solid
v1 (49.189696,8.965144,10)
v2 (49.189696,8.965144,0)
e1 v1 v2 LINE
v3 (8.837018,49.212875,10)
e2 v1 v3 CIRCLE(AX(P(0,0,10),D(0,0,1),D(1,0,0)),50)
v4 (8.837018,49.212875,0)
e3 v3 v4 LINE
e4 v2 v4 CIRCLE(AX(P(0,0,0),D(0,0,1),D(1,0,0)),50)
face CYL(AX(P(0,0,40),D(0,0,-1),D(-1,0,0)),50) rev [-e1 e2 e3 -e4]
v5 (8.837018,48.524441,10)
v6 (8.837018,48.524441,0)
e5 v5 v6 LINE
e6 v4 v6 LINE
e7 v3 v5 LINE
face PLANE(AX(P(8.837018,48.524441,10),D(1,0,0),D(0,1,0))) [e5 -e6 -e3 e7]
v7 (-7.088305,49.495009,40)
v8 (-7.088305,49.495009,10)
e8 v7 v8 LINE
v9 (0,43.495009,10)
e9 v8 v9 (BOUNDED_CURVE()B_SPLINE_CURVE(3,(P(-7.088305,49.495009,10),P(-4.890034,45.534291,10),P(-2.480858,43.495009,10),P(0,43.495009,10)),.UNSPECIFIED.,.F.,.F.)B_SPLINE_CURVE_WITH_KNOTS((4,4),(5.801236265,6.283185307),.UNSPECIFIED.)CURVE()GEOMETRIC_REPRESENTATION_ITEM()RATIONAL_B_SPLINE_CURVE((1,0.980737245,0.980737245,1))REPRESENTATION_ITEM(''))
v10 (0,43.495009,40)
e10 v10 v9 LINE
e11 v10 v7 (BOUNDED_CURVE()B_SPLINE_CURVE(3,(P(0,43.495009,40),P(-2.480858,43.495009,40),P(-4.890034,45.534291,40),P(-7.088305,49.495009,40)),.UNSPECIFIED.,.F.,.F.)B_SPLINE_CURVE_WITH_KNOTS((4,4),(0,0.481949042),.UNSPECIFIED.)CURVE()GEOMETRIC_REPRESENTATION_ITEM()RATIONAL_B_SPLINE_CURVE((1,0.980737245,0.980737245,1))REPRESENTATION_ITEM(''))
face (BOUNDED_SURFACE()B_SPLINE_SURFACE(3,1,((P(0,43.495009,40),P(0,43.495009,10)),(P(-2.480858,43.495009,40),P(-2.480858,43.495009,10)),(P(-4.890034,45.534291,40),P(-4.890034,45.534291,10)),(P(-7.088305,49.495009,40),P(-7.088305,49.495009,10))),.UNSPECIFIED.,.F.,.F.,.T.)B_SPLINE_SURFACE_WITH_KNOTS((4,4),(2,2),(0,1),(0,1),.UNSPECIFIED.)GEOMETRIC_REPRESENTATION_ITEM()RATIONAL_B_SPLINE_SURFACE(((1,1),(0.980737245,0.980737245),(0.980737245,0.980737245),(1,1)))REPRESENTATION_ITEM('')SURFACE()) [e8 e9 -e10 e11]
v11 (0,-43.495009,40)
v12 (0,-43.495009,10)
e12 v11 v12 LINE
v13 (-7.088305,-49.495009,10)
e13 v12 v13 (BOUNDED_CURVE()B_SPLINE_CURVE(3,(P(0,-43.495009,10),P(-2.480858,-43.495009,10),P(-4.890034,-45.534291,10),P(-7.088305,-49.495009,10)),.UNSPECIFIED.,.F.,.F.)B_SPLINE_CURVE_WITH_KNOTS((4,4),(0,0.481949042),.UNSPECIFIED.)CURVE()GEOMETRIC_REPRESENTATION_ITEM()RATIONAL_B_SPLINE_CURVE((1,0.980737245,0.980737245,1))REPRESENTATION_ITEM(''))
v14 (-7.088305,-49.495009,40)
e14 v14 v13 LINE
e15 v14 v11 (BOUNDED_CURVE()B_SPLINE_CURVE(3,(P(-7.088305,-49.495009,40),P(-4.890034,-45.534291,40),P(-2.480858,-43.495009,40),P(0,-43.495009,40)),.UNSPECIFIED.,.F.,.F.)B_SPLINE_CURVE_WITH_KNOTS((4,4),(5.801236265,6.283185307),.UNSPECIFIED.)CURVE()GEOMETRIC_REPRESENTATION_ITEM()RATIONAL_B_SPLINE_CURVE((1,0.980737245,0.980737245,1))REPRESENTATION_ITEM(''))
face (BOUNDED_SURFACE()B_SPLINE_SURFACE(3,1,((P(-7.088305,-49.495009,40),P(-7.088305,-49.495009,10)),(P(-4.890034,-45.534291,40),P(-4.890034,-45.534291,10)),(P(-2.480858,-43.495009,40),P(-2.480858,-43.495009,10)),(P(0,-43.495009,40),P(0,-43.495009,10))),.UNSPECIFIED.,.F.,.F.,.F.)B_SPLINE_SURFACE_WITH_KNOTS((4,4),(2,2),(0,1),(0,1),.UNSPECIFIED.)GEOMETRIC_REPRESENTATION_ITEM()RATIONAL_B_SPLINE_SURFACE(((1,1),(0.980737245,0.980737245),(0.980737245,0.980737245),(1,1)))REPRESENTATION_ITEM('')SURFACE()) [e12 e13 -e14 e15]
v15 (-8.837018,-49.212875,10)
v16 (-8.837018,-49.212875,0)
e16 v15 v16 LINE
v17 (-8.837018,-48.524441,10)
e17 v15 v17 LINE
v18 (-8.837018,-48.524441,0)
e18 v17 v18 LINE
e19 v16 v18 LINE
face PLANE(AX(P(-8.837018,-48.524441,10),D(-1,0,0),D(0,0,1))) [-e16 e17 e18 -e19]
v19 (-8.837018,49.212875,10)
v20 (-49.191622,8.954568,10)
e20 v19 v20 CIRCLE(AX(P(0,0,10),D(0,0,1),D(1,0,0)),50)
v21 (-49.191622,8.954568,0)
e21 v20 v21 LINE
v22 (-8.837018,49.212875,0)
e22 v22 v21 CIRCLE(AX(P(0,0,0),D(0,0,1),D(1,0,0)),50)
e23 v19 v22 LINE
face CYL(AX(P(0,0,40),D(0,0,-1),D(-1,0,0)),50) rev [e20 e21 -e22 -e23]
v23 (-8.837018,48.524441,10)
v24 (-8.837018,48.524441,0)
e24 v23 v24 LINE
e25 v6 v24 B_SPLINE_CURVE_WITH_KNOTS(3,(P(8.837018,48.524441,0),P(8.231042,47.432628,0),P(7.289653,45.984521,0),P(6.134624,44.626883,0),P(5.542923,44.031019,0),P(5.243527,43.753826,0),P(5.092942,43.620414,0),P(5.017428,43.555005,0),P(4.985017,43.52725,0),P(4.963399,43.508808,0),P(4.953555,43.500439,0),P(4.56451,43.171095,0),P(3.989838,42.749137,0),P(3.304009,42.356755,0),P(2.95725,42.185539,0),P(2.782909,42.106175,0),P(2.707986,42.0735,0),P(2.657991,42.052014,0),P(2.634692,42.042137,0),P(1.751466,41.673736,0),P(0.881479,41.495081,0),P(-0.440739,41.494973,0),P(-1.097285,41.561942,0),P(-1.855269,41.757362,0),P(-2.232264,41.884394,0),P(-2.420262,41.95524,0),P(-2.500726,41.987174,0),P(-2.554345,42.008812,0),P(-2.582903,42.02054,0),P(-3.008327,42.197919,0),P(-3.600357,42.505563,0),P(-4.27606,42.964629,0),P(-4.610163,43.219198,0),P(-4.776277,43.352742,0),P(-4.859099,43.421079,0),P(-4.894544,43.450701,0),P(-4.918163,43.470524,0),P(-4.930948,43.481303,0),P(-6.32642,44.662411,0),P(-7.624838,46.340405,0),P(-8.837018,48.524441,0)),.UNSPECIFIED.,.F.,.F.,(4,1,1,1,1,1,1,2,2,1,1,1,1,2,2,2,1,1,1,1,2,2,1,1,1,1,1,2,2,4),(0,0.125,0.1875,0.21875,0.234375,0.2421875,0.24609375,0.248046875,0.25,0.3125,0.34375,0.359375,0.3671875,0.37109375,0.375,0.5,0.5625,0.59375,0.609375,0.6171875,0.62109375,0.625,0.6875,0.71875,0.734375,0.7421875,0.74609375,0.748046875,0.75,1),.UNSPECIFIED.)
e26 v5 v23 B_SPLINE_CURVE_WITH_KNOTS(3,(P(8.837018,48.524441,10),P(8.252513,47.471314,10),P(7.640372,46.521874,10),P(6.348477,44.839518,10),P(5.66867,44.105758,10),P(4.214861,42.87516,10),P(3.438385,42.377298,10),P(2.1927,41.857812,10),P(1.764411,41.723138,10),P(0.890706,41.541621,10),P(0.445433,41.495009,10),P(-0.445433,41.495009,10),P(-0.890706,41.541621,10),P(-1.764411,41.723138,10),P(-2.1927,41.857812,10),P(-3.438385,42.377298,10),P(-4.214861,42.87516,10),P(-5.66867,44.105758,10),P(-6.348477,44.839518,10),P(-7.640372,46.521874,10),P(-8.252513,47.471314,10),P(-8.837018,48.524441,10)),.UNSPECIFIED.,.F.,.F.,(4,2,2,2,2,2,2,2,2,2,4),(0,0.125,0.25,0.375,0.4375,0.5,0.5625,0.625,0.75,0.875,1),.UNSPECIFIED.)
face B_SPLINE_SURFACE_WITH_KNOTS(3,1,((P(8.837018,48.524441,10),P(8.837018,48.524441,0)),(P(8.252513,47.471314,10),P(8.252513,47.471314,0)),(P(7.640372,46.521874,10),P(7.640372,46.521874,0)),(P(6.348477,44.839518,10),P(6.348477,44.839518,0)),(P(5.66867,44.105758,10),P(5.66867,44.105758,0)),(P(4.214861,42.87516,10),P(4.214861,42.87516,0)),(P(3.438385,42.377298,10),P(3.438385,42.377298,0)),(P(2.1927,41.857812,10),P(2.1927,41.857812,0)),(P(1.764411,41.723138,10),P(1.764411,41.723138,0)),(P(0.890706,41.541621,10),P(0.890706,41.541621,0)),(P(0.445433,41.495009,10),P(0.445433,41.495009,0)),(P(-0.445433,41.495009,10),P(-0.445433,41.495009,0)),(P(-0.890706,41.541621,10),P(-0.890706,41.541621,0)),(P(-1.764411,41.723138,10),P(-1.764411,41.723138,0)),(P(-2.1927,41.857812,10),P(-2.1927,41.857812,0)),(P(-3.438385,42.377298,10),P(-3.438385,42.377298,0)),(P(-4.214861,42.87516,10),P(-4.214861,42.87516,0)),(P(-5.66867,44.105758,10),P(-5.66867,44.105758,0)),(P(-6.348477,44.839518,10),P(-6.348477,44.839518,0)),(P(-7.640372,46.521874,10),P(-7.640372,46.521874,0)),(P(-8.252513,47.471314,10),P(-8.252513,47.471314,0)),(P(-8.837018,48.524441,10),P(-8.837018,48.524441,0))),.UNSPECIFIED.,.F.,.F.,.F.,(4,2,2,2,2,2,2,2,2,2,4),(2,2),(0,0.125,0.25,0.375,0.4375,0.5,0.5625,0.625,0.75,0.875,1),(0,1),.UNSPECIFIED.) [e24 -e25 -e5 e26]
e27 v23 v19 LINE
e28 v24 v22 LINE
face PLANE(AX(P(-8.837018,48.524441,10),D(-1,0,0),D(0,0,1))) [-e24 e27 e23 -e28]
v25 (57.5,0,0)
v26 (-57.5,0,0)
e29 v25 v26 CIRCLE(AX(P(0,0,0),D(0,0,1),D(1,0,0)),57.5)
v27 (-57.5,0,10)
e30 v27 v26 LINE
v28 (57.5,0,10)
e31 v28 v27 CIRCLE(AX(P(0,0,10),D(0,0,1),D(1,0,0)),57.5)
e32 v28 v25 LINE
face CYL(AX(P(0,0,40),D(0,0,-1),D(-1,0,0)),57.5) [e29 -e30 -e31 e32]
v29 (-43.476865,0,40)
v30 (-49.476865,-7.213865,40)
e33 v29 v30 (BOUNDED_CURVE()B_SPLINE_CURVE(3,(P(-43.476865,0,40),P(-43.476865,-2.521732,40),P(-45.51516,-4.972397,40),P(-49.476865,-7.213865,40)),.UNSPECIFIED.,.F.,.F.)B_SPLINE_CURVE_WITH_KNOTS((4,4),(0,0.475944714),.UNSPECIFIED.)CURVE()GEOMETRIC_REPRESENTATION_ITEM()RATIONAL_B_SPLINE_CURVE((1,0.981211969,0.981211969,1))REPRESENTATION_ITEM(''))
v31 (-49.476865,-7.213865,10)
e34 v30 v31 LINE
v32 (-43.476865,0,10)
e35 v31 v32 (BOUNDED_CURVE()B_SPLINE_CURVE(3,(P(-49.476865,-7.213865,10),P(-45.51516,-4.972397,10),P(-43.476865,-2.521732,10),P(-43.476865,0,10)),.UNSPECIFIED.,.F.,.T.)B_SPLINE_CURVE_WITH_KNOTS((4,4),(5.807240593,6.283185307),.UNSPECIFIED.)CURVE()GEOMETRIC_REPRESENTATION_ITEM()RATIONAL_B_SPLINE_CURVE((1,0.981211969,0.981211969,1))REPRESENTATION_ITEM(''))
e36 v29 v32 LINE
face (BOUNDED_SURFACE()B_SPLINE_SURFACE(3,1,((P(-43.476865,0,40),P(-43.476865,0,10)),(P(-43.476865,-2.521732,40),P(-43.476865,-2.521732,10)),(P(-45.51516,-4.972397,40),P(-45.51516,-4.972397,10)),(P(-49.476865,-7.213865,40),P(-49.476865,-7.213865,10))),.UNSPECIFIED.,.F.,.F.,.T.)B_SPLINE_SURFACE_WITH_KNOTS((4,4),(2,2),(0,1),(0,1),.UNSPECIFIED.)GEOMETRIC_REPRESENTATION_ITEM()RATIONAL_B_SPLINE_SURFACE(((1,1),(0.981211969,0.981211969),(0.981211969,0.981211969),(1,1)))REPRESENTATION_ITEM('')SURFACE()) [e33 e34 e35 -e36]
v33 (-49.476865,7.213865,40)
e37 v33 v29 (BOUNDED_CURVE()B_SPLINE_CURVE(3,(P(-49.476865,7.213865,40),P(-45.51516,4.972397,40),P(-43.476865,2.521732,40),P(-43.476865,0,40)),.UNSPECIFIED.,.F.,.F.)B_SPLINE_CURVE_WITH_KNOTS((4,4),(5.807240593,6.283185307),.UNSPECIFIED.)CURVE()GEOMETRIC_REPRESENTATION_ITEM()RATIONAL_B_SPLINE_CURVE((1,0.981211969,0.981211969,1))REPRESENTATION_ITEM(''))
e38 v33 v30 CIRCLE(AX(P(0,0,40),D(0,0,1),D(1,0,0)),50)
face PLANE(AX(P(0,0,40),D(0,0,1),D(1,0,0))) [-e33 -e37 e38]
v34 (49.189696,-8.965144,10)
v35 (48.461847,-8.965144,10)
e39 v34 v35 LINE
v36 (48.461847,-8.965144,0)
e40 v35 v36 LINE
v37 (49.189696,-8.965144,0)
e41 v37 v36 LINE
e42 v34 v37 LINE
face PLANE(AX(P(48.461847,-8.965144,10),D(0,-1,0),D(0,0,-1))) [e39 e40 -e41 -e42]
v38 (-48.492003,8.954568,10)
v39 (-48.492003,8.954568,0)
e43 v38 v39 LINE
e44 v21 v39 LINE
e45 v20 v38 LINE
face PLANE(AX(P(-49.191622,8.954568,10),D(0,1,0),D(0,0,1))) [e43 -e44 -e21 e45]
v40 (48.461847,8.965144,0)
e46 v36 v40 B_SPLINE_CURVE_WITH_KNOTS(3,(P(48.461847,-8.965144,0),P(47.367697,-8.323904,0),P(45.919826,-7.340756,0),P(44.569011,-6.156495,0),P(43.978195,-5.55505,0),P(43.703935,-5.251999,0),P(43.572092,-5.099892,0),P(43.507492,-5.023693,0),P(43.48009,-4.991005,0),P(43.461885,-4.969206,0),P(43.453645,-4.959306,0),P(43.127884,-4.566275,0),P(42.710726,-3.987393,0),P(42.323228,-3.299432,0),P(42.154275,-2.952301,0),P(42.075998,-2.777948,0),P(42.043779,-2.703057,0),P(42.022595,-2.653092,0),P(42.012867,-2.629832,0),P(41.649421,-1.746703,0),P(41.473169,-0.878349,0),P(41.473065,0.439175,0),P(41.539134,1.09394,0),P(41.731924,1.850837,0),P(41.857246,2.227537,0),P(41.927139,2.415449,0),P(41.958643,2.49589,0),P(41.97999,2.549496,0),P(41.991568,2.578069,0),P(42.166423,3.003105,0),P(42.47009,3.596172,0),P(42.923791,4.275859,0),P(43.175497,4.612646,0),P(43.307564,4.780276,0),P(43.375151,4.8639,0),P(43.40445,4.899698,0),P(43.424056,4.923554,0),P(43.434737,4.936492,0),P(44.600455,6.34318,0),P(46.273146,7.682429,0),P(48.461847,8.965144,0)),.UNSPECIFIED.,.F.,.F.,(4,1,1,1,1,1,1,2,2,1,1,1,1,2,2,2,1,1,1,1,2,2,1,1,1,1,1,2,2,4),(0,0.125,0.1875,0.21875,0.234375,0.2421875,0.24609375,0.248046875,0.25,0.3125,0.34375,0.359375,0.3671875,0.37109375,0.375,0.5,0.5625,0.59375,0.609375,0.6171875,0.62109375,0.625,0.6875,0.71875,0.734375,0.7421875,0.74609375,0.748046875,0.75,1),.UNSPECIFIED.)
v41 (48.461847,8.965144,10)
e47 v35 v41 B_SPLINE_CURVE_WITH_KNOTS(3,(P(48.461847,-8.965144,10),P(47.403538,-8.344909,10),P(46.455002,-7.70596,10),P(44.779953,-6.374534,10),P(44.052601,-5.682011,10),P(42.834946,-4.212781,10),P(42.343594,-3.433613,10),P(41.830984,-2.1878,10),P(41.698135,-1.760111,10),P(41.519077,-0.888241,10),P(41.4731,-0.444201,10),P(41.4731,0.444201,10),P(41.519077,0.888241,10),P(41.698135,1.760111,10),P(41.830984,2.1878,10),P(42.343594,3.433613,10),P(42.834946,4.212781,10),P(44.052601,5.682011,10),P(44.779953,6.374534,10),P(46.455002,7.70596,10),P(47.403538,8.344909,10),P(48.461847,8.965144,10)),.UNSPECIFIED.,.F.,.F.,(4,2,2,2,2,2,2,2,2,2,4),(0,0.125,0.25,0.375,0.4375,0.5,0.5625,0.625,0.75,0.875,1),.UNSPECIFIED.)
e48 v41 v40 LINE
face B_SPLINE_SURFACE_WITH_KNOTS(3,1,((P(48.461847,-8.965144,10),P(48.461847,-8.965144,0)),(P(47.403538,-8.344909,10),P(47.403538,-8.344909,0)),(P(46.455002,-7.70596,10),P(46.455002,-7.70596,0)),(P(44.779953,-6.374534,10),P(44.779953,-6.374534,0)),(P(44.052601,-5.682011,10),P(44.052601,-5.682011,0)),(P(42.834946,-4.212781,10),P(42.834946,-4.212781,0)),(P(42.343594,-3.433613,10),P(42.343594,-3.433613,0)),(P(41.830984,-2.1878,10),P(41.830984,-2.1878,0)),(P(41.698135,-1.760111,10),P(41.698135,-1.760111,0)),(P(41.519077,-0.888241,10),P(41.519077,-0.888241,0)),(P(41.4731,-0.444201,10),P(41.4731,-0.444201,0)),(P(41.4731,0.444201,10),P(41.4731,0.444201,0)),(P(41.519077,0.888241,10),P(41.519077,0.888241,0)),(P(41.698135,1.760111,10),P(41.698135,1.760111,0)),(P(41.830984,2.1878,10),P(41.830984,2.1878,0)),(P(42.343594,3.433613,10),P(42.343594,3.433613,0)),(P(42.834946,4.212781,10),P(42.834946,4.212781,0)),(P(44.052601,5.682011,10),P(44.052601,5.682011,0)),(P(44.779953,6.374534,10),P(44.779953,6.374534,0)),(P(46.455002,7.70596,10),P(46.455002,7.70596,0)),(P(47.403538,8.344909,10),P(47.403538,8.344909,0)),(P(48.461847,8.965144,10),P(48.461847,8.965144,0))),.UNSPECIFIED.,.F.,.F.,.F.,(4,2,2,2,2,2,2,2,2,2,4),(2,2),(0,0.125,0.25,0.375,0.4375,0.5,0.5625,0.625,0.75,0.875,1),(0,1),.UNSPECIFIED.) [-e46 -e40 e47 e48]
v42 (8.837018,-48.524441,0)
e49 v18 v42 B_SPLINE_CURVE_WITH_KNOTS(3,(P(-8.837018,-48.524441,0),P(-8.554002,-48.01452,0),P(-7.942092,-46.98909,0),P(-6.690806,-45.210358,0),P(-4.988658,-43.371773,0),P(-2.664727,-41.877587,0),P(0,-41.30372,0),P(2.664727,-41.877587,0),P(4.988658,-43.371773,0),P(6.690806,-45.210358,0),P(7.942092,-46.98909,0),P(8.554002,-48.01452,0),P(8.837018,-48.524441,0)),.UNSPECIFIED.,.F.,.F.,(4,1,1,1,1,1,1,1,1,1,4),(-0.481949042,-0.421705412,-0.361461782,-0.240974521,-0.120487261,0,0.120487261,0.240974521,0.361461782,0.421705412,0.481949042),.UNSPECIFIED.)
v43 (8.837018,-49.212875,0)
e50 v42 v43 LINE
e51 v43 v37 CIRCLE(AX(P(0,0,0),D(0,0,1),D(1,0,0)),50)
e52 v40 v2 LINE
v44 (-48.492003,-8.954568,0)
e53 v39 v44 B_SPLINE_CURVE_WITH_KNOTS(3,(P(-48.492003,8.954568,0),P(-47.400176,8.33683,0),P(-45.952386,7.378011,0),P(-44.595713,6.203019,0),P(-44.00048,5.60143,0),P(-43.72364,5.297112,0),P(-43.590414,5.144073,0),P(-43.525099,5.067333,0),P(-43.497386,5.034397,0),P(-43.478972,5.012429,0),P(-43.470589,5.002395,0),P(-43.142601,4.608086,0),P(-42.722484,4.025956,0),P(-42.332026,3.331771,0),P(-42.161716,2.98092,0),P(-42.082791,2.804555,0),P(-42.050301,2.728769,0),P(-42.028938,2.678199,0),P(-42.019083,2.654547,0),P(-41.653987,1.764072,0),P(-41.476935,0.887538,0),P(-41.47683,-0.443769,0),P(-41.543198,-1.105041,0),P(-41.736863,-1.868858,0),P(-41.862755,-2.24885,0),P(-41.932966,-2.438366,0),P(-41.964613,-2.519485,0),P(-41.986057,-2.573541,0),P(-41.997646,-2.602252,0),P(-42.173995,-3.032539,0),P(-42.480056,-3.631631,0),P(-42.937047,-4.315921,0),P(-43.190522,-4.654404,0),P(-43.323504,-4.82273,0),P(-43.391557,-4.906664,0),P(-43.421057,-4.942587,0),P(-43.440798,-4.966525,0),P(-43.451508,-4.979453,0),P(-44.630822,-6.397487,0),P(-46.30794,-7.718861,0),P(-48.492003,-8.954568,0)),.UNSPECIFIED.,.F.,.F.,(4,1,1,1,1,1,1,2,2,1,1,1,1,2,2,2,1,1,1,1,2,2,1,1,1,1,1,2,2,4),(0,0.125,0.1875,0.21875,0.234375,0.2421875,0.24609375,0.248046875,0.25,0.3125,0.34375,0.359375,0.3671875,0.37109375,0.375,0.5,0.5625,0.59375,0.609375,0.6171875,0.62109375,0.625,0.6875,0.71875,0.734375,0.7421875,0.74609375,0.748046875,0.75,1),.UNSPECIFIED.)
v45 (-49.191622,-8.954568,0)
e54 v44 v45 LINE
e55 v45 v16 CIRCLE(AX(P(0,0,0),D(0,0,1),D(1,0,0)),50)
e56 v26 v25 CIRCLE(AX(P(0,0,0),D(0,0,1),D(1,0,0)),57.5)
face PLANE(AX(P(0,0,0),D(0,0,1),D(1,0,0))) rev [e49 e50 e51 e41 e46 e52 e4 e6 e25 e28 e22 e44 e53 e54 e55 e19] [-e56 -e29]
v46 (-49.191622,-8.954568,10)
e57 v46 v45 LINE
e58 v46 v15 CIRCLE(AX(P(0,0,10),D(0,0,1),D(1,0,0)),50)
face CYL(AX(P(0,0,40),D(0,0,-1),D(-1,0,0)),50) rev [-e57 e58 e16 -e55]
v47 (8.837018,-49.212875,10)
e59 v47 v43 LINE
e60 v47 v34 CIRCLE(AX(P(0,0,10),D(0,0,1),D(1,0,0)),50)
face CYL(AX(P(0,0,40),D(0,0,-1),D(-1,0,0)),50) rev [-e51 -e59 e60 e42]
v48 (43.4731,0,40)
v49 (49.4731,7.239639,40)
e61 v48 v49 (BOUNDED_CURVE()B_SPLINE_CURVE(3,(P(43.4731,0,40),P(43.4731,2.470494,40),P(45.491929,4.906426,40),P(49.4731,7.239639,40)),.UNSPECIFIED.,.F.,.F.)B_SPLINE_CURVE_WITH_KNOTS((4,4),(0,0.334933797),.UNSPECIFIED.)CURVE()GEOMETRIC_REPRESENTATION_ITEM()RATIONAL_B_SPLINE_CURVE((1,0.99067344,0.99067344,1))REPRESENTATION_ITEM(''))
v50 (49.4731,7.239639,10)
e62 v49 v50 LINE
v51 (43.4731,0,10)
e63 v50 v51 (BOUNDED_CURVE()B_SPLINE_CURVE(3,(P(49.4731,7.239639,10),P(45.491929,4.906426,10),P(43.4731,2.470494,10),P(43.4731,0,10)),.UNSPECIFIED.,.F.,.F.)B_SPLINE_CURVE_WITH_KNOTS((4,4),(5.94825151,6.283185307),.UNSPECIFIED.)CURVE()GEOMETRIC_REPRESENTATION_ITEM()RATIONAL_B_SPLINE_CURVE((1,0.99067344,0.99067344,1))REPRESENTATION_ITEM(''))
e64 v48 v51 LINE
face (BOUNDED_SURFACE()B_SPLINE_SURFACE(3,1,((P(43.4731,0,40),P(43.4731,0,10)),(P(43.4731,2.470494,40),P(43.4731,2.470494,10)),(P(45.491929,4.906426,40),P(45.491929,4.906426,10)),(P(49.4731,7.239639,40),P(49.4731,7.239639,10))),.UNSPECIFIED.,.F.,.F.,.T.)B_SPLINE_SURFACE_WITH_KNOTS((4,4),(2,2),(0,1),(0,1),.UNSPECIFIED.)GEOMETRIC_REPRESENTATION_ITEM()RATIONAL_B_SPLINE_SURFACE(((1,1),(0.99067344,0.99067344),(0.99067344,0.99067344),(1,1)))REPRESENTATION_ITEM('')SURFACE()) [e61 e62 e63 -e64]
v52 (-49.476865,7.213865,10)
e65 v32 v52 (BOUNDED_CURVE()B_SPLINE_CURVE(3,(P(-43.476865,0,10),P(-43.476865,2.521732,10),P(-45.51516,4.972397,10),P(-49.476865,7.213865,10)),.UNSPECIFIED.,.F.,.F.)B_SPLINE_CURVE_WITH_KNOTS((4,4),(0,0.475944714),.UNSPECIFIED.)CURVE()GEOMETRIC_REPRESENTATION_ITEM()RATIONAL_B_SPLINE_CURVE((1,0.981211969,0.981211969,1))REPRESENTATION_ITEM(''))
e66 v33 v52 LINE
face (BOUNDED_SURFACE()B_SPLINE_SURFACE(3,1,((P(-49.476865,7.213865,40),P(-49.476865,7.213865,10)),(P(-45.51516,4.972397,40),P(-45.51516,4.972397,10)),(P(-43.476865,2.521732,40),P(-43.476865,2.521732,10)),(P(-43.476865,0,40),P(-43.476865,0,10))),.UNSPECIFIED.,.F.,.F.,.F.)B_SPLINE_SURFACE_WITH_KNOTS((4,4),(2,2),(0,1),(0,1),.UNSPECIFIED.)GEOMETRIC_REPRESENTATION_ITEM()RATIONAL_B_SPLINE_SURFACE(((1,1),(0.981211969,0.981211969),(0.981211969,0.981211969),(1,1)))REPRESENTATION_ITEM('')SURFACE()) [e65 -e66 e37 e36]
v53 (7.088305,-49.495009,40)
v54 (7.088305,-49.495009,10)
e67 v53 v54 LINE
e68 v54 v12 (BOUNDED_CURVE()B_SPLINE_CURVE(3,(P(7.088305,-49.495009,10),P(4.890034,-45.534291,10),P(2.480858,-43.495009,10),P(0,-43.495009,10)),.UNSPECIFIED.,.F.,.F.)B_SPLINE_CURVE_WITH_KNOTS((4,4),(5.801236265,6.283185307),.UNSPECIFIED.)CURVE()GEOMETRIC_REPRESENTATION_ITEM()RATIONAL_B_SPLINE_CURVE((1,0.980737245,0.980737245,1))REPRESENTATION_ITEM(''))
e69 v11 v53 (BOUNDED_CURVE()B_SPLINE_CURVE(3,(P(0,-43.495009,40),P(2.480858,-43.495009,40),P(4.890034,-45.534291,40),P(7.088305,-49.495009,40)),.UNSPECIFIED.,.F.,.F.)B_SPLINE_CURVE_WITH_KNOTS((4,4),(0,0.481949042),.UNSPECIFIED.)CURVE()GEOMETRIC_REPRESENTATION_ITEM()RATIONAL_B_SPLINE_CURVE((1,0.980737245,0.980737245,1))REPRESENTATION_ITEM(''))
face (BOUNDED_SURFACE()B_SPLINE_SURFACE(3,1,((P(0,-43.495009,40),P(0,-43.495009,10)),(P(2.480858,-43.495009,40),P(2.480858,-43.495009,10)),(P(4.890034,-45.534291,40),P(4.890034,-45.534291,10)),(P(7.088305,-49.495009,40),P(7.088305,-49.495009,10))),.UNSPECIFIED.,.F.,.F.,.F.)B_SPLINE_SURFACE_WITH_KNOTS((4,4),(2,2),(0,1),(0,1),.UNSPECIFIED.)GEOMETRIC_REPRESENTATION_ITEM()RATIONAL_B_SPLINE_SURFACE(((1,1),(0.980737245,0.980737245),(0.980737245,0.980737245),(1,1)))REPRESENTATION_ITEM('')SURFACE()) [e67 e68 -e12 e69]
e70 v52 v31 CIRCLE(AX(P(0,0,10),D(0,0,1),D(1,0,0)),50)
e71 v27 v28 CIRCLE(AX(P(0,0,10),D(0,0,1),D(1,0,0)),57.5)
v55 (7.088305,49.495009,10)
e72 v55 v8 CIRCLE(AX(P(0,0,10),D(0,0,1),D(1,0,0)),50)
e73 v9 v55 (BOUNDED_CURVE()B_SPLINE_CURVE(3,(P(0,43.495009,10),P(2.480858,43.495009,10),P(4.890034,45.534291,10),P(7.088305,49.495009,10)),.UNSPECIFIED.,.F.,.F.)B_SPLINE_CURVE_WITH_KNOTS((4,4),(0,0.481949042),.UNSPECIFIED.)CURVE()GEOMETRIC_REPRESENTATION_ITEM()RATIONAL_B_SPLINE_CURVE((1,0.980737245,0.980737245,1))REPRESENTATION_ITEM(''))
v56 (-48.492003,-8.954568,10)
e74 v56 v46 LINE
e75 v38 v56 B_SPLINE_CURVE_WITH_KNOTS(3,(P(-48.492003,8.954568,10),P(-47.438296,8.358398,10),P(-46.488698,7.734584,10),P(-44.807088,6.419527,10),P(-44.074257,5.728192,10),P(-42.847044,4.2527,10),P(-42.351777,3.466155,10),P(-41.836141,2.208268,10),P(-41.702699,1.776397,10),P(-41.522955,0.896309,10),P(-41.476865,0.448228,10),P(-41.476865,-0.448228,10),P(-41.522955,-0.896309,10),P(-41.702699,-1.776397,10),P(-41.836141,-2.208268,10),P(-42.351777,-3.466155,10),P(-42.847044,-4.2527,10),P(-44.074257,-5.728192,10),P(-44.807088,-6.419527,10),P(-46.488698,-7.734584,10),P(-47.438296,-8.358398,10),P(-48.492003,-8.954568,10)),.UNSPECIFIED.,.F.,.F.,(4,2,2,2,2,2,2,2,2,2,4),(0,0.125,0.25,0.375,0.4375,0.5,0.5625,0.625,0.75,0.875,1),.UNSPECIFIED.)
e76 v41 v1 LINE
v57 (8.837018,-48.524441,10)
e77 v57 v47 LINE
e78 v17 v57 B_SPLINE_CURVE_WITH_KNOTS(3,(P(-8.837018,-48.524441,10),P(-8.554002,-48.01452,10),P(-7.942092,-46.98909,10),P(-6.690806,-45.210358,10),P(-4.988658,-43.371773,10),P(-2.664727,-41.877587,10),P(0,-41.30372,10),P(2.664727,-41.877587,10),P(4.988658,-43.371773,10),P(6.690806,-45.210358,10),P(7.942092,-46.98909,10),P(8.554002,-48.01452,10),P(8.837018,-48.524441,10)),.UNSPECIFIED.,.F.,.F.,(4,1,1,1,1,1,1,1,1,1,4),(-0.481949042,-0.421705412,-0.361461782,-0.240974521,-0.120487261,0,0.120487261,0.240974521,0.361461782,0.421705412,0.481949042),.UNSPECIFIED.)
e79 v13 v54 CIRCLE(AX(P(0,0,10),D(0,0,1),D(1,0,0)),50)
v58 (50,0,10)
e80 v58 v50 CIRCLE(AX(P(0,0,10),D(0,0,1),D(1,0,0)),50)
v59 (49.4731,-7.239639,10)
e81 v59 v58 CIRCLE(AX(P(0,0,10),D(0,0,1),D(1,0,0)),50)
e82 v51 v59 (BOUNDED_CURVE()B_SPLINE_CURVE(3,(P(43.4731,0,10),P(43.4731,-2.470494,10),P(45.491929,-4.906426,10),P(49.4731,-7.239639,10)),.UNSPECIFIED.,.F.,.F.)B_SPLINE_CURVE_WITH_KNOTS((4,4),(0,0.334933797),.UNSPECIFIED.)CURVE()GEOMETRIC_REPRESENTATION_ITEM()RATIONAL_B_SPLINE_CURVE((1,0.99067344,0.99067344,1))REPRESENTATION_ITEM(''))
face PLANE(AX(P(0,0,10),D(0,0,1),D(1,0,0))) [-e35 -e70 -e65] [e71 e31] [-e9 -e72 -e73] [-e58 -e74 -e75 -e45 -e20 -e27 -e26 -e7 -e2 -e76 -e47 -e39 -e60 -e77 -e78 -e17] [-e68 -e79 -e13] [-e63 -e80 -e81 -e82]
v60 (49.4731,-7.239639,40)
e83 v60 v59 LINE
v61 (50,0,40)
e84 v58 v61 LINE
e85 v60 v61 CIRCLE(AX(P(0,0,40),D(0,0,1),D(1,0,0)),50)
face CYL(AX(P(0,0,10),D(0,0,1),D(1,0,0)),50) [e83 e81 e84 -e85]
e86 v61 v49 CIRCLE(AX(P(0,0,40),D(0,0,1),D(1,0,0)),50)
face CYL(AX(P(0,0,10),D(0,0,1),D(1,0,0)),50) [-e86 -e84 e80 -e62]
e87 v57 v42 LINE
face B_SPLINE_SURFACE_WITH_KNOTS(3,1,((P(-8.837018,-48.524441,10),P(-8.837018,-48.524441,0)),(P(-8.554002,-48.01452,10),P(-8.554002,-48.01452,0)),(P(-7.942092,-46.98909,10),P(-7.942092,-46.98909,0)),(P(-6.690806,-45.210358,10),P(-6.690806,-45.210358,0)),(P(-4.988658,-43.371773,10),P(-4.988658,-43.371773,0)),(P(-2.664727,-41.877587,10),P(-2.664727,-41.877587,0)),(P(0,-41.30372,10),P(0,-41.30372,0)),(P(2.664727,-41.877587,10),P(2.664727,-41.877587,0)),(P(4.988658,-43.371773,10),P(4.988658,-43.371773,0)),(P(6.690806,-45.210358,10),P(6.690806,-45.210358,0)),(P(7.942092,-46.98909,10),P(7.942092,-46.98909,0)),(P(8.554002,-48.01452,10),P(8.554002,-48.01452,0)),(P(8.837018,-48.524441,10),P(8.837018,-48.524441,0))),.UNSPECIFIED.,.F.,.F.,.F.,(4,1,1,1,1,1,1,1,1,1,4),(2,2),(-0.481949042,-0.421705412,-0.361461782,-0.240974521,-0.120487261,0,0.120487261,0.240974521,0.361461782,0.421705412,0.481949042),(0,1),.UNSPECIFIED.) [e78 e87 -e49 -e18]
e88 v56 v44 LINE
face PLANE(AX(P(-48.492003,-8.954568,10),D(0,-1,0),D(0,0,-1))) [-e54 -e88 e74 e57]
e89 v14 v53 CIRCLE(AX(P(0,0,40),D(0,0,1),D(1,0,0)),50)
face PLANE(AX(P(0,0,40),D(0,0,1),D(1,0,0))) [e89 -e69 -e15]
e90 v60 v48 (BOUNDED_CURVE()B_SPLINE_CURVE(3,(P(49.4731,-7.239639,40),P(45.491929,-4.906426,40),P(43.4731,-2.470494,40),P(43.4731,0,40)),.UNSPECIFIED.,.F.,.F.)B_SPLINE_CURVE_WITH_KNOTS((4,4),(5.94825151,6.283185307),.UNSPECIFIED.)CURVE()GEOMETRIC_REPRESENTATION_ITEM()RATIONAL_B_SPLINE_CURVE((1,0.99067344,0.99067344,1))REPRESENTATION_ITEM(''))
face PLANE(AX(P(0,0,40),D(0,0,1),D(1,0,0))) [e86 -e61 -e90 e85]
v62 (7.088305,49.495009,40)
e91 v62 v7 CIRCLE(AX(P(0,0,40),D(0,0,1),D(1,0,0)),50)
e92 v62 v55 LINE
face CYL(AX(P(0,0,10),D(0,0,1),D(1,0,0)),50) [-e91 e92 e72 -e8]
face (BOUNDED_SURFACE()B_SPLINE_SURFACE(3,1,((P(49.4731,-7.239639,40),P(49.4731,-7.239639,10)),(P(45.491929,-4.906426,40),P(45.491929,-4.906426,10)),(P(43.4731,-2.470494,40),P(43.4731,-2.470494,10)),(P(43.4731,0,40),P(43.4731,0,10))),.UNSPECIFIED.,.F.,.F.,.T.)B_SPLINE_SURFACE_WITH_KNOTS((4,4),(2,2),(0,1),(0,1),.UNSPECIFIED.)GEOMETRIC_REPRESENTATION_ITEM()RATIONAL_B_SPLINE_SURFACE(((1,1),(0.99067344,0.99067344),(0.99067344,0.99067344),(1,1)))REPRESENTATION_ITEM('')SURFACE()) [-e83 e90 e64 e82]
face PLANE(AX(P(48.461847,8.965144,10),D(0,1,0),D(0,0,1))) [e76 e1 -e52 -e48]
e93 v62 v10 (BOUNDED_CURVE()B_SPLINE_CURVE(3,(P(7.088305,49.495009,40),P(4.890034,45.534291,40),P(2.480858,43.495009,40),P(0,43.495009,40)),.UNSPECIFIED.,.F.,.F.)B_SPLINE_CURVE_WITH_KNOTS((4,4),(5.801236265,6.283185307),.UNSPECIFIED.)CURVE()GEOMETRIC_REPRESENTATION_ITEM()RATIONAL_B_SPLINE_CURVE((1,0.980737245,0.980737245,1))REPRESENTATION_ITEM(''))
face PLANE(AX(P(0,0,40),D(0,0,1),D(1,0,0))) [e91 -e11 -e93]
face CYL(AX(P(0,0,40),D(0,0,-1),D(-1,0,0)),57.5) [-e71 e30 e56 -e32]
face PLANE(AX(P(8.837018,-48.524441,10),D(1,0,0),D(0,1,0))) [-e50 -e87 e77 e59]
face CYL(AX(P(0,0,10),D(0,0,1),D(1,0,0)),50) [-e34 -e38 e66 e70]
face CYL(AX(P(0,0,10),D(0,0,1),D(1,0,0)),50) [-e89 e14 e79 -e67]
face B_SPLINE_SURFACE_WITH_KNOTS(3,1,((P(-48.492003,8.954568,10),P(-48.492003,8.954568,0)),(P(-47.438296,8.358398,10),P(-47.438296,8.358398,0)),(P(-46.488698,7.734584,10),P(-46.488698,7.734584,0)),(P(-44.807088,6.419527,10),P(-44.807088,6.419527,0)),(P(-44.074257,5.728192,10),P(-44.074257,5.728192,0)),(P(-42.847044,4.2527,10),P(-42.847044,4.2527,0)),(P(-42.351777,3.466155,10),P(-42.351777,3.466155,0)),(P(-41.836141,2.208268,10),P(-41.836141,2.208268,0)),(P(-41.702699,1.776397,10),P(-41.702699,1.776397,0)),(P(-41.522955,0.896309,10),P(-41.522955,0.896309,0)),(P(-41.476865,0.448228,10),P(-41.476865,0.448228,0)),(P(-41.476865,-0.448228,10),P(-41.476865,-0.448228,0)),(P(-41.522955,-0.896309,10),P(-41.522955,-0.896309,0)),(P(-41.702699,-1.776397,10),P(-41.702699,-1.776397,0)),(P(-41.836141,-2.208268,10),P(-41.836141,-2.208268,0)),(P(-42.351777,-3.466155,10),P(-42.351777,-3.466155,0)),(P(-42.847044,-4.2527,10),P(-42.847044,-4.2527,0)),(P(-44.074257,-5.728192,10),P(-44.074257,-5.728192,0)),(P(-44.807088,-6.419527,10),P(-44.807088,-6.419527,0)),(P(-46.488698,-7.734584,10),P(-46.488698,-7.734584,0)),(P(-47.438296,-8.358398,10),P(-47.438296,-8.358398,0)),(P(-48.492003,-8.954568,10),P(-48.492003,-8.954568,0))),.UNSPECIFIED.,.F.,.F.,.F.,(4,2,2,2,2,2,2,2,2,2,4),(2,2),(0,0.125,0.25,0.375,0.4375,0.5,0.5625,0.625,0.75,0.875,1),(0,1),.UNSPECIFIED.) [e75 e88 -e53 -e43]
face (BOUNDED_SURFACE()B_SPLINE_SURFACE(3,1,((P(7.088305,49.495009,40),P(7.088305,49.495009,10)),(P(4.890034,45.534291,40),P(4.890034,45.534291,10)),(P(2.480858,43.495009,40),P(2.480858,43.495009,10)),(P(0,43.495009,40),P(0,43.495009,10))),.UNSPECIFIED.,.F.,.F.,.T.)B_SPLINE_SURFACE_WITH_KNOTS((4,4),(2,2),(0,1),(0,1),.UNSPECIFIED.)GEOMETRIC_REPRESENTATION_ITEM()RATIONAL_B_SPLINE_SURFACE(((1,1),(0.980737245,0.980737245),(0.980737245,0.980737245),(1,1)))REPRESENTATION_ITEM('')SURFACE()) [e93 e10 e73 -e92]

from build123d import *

# Parameters (mm, degrees)
SKETCH_1_R          = 57.5
EXTRUDE_1_DEPTH     = 40
CUT_EXTRUDE_START   = -30
SKETCH_2_R          = 60
SKETCH_2_R_2        = 50
CUT_EXTRUDE_3_DEPTH = 30
EXTRUDE_3_DEPTH     = 10
EXTRUDE_4_DEPTH     = 10
EXTRUDE_5_DEPTH     = 10
EXTRUDE_6_DEPTH     = 10


with BuildPart() as part:
    # 草图1 → 拉伸1 (new body)
    with BuildSketch(Plane.XY):
        Circle(SKETCH_1_R)
        with BuildLine():
            ThreePointArc((-7.088304974, 49.495009169), (-35.310457237, 35.400163978), (-49.476864779, 7.213865238))
            add(Edge.make_bspline(
                [(-49.476864779, -7.213865238), (-36.726647454, 0), (-49.476864779, 7.213865238)],
                knots=[5.807240593, 5.807240593, 5.807240593, 6.759130021, 6.759130021, 6.759130021], degree=2, weights=[1, 0.888860271, 1]))
            ThreePointArc((-49.476864779, -7.213865238), (-35.310457237, -35.400163978), (-7.088304974, -49.495009169))
            add(Edge.make_bspline(
                [(7.088304974, -49.495009169), (0, -36.723712512), (-7.088304974, -49.495009169)],
                knots=[5.801236265, 5.801236265, 5.801236265, 6.76513435, 6.76513435, 6.76513435], degree=2, weights=[1, 0.886093211, 1]))
            ThreePointArc((7.088304974, -49.495009169), (35.301235246, -35.409360205), (49.473100028, -7.239639051))
            add(Edge.make_bspline(
                [(49.473100028, 7.239639051), (37.120075632, 0), (49.473100028, -7.239639051)],
                knots=[2.806658856, 2.806658856, 2.806658856, 3.476526451, 3.476526451, 3.476526451], degree=2, weights=[1, 0.944432073, 1]))
            ThreePointArc((49.473100028, 7.239639051), (35.301235246, 35.409360205), (7.088304974, 49.495009169))
            add(Edge.make_bspline(
                [(-7.088304974, 49.495009169), (0, 36.723712512), (7.088304974, 49.495009169)],
                knots=[2.659643611, 2.659643611, 2.659643611, 3.623541696, 3.623541696, 3.623541696], degree=2, weights=[1, 0.886093211, 1]))
        make_face(mode=Mode.SUBTRACT)
    extrude(amount=EXTRUDE_1_DEPTH)

    # 草图2 → 拉伸3 (cut)
    with BuildSketch(Plane.XY.offset(40).offset(CUT_EXTRUDE_START)):
        Circle(SKETCH_2_R)
        Circle(SKETCH_2_R_2, mode=Mode.SUBTRACT)
    extrude(amount=CUT_EXTRUDE_3_DEPTH, mode=Mode.SUBTRACT)

    # 草图5 → 凸台-拉伸3 (add)
    with BuildSketch(Plane(origin=(0, 0, 0), x_dir=(-1, 0, 0), z_dir=(0, 0, -1))):
        with BuildLine():
            Line((49.191622289, 8.954568475), (48.492003246, 8.954568475))
            add(Edge.make_bspline(
                [(48.492003246, 8.954568475), (47.438295788, 8.358397963), (46.488698256, 7.73458393), (44.807087954, 6.419527471), (44.074256872, 5.72819176), (42.847043729, 4.252700055), (42.351776591, 3.466154718), (41.836140902, 2.208267679), (41.702698746, 1.776396531), (41.522955051, 0.896309015), (41.476864779, 0.448228181), (41.476864779, -0.448228181), (41.522955051, -0.896309015), (41.702698746, -1.776396531), (41.836140902, -2.208267679), (42.351776591, -3.466154718), (42.847043729, -4.252700055), (44.074256872, -5.72819176), (44.807087954, -6.419527471), (46.488698256, -7.73458393), (47.438295788, -8.358397963), (48.492003246, -8.954568475)],
                knots=[0, 0, 0, 0, 0.125, 0.125, 0.25, 0.25, 0.375, 0.375, 0.4375, 0.4375, 0.5, 0.5, 0.5625, 0.5625, 0.625, 0.625, 0.75, 0.75, 0.875, 0.875, 1, 1, 1, 1], degree=3))
            Line((48.492003246, -8.954568475), (49.191622289, -8.954568475))
            ThreePointArc((49.191622289, -8.954568475), (49.341920281, -8.085474816), (49.476864779, -7.213865238))
            add(Edge.make_bspline(
                [(49.476864779, 7.213865238), (36.726647454, 0), (49.476864779, -7.213865238)],
                knots=[5.807240593, 5.807240593, 5.807240593, 6.759130021, 6.759130021, 6.759130021], degree=2, weights=[1, 0.888860271, 1]))
            ThreePointArc((49.476864779, 7.213865238), (49.341920281, 8.085474816), (49.191622289, 8.954568475))
        make_face()
    extrude(amount=-EXTRUDE_3_DEPTH)

    # 草图7 → 凸台-拉伸4 (add)
    with BuildSketch(Plane(origin=(0, 0, 0), x_dir=(-1, 0, 0), z_dir=(0, 0, -1))):
        with BuildLine():
            Line((-8.837018132, -48.524441143), (-8.837018132, -49.212875455))
            ThreePointArc((-8.837018132, -49.212875455), (-7.963911028, -49.361686774), (-7.088304974, -49.495009169))
            add(Edge.make_bspline(
                [(7.088304974, -49.495009169), (0, -36.723712512), (-7.088304974, -49.495009169)],
                knots=[5.801236265, 5.801236265, 5.801236265, 6.76513435, 6.76513435, 6.76513435], degree=2, weights=[1, 0.886093211, 1]))
            ThreePointArc((7.088304974, -49.495009169), (7.963911028, -49.361686774), (8.837018132, -49.212875455))
            Line((8.837018132, -49.212875455), (8.837018132, -48.524441143))
            add(Edge.make_bspline(
                [(8.837018132, -48.524441143), (8.554002496, -48.014519989), (7.94209171, -46.989090119), (6.690805785, -45.210357531), (4.988657794, -43.371772875), (2.66472736, -41.877587359), (0, -41.303720073), (-2.66472736, -41.877587359), (-4.988657794, -43.371772875), (-6.690805785, -45.210357531), (-7.94209171, -46.989090119), (-8.554002496, -48.014519989), (-8.837018132, -48.524441143)],
                knots=[-0.481949042, -0.481949042, -0.481949042, -0.481949042, -0.421705412, -0.361461782, -0.240974521, -0.120487261, 0, 0.120487261, 0.240974521, 0.361461782, 0.421705412, 0.481949042, 0.481949042, 0.481949042, 0.481949042], degree=3))
        make_face()
    extrude(amount=-EXTRUDE_4_DEPTH)

    # 草图8 → 凸台-拉伸5 (add)
    with BuildSketch(Plane(origin=(0, 0, 0), x_dir=(-1, 0, 0), z_dir=(0, 0, -1))):
        with BuildLine():
            Line((-48.461847021, 8.965144008), (-49.189696003, 8.965144008))
            ThreePointArc((-49.189696003, 8.965144008), (-49.33894174, 8.103630542), (-49.473100028, 7.239639051))
            add(Edge.make_bspline(
                [(-49.473100028, -7.239639051), (-37.120075632, 0), (-49.473100028, 7.239639051)],
                knots=[2.806658856, 2.806658856, 2.806658856, 3.476526451, 3.476526451, 3.476526451], degree=2, weights=[1, 0.944432073, 1]))
            ThreePointArc((-49.473100028, -7.239639051), (-49.33894174, -8.103630542), (-49.189696003, -8.965144008))
            Line((-49.189696003, -8.965144008), (-48.461847021, -8.965144008))
            add(Edge.make_bspline(
                [(-48.461847021, -8.965144008), (-47.403537543, -8.344908965), (-46.455001816, -7.705959573), (-44.77995312, -6.374534454), (-44.052601357, -5.682011491), (-42.834946416, -4.212781113), (-42.343593905, -3.433612838), (-41.830983832, -2.187799789), (-41.698135209, -1.760111418), (-41.519077327, -0.888240926), (-41.473100028, -0.444200971), (-41.473100028, 0.444200971), (-41.519077327, 0.888240926), (-41.698135209, 1.760111418), (-41.830983832, 2.187799789), (-42.343593905, 3.433612838), (-42.834946416, 4.212781113), (-44.052601357, 5.682011491), (-44.77995312, 6.374534454), (-46.455001816, 7.705959573), (-47.403537543, 8.344908965), (-48.461847021, 8.965144008)],
                knots=[0, 0, 0, 0, 0.125, 0.125, 0.25, 0.25, 0.375, 0.375, 0.4375, 0.4375, 0.5, 0.5, 0.5625, 0.5625, 0.625, 0.625, 0.75, 0.75, 0.875, 0.875, 1, 1, 1, 1], degree=3))
        make_face()
    extrude(amount=-EXTRUDE_5_DEPTH)

    # 草图9 → 凸台-拉伸6 (add)
    with BuildSketch(Plane(origin=(0, 0, 0), x_dir=(-1, 0, 0), z_dir=(0, 0, -1))):
        with BuildLine():
            Line((-8.837018132, 48.524441143), (-8.837018132, 49.212875455))
            ThreePointArc((-8.837018132, 49.212875455), (-7.963911028, 49.361686774), (-7.088304974, 49.495009169))
            add(Edge.make_bspline(
                [(-7.088304974, 49.495009169), (0, 36.723712512), (7.088304974, 49.495009169)],
                knots=[5.801236265, 5.801236265, 5.801236265, 6.76513435, 6.76513435, 6.76513435], degree=2, weights=[1, 0.886093211, 1]))
            ThreePointArc((7.088304974, 49.495009169), (7.963911028, 49.361686774), (8.837018132, 49.212875455))
            Line((8.837018132, 49.212875455), (8.837018132, 48.524441143))
            add(Edge.make_bspline(
                [(-8.837018132, 48.524441143), (-8.25251339, 47.471314411), (-7.640371758, 46.521874102), (-6.348477364, 44.839518065), (-5.668669979, 44.105757745), (-4.214861328, 42.875160029), (-3.438384565, 42.377297638), (-2.192699526, 41.857811777), (-1.764410814, 41.7231382), (-0.890706349, 41.541621262), (-0.445433319, 41.495009169), (0.445433319, 41.495009169), (0.890706349, 41.541621262), (1.764410814, 41.7231382), (2.192699526, 41.857811777), (3.438384565, 42.377297638), (4.214861328, 42.875160029), (5.668669979, 44.105757745), (6.348477364, 44.839518065), (7.640371758, 46.521874102), (8.25251339, 47.471314411), (8.837018132, 48.524441143)],
                knots=[0, 0, 0, 0, 0.125, 0.125, 0.25, 0.25, 0.375, 0.375, 0.4375, 0.4375, 0.5, 0.5, 0.5625, 0.5625, 0.625, 0.625, 0.75, 0.75, 0.875, 0.875, 1, 1, 1, 1], degree=3))
        make_face()
    extrude(amount=-EXTRUDE_6_DEPTH)


solid = part.part
